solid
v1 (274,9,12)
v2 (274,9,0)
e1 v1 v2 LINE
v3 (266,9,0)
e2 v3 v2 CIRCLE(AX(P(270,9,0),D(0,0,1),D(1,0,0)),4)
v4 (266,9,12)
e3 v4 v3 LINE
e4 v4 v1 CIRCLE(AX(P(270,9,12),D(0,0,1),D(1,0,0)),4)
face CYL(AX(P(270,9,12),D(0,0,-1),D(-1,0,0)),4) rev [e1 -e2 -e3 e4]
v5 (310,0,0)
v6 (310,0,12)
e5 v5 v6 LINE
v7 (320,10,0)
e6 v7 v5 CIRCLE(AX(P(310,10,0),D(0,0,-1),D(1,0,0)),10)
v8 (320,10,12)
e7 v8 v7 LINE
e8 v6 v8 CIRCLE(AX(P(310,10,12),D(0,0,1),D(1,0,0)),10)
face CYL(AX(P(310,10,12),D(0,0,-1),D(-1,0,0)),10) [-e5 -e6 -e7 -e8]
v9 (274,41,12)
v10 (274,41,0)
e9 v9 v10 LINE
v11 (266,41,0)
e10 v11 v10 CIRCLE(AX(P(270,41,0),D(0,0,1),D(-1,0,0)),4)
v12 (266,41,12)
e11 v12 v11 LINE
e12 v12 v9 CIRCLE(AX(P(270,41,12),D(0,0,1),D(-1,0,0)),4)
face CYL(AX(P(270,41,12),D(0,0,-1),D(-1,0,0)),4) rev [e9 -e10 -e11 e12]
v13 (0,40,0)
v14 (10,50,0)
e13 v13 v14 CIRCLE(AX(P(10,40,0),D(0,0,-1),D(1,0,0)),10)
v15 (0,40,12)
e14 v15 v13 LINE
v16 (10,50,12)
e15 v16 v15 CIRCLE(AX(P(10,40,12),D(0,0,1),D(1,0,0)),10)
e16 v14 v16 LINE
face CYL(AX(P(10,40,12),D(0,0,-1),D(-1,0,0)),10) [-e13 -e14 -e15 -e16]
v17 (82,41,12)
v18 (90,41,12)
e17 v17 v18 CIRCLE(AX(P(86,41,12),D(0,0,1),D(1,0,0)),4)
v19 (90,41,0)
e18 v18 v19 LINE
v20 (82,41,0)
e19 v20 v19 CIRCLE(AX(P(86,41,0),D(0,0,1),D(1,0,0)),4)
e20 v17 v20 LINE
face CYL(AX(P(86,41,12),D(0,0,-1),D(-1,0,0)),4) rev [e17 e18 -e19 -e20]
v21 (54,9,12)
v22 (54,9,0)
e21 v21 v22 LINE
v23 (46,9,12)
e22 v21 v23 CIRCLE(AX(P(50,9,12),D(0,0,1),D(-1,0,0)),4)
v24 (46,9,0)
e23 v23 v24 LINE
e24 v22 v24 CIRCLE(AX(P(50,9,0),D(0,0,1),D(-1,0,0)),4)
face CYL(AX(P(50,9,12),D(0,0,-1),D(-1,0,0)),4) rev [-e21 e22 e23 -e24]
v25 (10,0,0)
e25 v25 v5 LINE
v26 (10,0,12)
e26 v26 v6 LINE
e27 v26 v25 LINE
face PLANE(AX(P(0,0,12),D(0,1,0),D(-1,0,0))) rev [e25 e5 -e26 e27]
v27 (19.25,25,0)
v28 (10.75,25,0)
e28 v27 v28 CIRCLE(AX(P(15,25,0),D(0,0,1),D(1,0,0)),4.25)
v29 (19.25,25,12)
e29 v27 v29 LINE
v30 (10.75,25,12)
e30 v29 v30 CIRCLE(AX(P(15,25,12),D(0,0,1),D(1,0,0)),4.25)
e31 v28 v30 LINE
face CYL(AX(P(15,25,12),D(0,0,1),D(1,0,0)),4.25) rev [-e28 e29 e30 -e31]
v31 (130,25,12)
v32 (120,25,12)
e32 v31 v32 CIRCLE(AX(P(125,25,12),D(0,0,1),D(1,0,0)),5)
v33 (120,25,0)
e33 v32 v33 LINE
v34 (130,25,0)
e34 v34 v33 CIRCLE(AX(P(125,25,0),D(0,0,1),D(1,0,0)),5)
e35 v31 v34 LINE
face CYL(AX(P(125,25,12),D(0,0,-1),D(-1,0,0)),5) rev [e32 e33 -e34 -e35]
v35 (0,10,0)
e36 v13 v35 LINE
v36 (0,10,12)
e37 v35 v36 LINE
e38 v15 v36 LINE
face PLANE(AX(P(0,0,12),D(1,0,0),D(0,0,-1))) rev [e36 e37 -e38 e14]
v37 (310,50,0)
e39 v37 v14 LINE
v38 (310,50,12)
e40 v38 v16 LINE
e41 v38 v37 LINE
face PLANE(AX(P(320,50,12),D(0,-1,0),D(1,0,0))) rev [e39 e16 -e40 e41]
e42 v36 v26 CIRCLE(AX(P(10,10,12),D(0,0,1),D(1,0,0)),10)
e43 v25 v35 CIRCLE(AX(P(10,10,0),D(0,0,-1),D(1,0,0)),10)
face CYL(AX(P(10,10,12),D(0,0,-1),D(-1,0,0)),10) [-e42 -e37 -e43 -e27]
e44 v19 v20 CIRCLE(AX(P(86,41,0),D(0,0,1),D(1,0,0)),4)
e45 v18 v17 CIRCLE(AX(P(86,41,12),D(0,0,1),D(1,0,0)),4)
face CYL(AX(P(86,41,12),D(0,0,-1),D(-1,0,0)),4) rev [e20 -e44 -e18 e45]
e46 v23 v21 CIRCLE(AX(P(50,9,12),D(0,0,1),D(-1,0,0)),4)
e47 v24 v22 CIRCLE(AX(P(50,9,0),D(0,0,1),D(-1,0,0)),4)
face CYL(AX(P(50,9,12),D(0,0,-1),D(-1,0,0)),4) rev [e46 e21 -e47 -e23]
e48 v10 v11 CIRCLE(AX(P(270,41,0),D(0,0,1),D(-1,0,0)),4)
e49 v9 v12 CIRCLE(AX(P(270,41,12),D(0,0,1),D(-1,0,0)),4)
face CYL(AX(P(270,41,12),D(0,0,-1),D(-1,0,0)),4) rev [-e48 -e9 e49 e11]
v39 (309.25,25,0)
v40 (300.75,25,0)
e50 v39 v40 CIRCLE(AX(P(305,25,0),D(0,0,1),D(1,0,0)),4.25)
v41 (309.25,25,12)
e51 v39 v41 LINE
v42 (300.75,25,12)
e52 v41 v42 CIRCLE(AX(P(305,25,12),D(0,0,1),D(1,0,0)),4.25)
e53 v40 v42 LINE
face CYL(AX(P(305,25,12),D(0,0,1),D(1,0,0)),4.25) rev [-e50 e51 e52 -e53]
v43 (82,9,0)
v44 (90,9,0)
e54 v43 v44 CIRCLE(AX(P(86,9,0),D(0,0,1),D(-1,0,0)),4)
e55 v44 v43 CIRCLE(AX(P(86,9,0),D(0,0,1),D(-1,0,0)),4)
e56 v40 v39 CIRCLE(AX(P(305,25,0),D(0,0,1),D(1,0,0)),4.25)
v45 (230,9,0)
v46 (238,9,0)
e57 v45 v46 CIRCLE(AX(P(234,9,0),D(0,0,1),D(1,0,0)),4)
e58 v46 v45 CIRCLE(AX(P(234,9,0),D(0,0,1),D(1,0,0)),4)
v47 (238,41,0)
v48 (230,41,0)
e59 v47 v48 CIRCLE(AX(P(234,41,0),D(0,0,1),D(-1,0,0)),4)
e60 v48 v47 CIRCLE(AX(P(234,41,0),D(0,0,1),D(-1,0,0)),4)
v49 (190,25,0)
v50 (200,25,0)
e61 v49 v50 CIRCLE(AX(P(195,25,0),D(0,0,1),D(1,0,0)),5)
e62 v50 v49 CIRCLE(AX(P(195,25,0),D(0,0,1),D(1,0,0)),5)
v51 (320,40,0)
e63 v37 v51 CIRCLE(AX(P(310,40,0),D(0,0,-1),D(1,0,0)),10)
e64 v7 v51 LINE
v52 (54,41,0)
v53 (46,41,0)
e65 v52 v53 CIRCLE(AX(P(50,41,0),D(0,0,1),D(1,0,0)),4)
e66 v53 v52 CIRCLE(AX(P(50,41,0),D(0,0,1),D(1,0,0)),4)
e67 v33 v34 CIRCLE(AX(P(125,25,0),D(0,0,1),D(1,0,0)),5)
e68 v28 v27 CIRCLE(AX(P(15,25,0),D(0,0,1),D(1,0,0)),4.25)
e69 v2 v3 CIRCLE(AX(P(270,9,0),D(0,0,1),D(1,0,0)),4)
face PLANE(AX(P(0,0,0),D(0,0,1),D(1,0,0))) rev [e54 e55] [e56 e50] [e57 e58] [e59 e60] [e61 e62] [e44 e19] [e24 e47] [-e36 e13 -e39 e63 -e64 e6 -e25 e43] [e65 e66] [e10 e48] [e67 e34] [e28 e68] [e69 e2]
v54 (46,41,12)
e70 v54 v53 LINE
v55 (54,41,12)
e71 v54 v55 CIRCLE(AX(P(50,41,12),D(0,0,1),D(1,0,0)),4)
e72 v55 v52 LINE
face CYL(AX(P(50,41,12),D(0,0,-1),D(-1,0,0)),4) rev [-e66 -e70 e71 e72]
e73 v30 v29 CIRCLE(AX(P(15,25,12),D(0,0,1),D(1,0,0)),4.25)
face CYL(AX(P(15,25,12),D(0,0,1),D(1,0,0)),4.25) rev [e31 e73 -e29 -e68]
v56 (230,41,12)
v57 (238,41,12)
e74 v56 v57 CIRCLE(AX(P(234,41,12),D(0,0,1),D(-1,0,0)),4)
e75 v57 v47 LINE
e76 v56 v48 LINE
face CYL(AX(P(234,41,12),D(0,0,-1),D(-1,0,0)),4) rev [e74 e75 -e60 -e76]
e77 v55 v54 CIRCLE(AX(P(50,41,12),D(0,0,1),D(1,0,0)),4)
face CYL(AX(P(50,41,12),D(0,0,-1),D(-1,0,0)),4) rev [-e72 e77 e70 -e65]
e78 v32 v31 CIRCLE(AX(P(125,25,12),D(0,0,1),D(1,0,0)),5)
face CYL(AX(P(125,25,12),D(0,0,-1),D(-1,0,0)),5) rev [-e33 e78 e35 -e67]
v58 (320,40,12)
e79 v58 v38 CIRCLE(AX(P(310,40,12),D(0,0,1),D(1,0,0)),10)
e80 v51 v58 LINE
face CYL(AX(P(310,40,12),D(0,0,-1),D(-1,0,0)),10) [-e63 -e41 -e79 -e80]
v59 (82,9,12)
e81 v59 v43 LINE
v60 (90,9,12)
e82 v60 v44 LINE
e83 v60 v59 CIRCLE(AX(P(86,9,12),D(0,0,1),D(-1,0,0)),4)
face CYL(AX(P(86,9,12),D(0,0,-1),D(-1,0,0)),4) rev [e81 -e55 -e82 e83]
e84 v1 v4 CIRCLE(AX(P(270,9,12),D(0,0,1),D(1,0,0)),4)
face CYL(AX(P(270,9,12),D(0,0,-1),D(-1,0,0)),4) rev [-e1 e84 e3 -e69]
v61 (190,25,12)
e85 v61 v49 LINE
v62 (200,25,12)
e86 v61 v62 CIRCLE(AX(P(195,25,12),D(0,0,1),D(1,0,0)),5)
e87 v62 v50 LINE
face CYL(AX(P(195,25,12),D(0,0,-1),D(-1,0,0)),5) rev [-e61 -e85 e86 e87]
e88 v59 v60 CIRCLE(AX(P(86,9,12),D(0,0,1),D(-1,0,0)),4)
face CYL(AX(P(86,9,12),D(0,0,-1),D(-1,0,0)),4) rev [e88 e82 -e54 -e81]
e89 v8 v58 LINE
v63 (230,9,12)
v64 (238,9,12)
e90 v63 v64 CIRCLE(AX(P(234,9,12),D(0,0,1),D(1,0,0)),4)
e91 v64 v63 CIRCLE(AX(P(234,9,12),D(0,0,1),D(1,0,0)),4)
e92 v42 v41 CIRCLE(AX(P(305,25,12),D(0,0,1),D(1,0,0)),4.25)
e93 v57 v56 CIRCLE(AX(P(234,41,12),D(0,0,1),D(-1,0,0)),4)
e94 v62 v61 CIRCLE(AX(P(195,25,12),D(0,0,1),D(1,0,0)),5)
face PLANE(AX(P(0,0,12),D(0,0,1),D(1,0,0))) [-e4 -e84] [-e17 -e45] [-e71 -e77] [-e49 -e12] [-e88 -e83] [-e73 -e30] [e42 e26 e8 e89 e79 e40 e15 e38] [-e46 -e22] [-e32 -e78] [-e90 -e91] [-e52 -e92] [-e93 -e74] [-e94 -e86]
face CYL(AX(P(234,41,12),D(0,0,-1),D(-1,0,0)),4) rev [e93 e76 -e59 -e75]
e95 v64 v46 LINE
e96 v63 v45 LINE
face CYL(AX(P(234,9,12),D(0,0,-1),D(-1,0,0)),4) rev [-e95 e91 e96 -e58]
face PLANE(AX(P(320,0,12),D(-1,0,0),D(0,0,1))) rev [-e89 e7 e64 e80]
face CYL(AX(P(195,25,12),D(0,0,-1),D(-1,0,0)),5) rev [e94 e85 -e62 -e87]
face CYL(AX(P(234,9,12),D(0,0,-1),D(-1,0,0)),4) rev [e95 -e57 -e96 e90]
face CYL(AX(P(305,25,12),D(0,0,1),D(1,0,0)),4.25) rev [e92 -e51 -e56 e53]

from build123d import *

# Parameters (mm, degrees)
SKETCH1_W              = 320
SKETCH1_H              = 50
SKETCH1_R              = 4
SKETCH1_R_2            = 5
BOSS_EXTRUDE1_DEPTH    = 12
M10_TAPPED_HOLE1_D     = 8.5
M10_TAPPED_HOLE1_DEPTH = 24.5
M10_TAPPED_HOLE1_TIP   = 2.553657631
FILLET1_R              = 10


with BuildPart() as part:
    # Sketch1 → Boss-Extrude1 (new body)
    with BuildSketch(Plane.XY):
        with Locations((160, 25)):
            Rectangle(SKETCH1_W, SKETCH1_H)
        with Locations((50, 41)):
            Circle(SKETCH1_R, mode=Mode.SUBTRACT)
        with Locations((86, 41)):
            Circle(SKETCH1_R, mode=Mode.SUBTRACT)
        with Locations(Location((86, 9, 0), (0, 0, 180))):
            Circle(SKETCH1_R, mode=Mode.SUBTRACT)
        with Locations(Location((50, 9, 0), (0, 0, 180))):
            Circle(SKETCH1_R, mode=Mode.SUBTRACT)
        with Locations((270, 9)):
            Circle(SKETCH1_R, mode=Mode.SUBTRACT)
        with Locations((234, 9)):
            Circle(SKETCH1_R, mode=Mode.SUBTRACT)
        with Locations(Location((234, 41, 0), (0, 0, 180))):
            Circle(SKETCH1_R, mode=Mode.SUBTRACT)
        with Locations(Location((270, 41, 0), (0, 0, 180))):
            Circle(SKETCH1_R, mode=Mode.SUBTRACT)
        with Locations((125, 25)):
            Circle(SKETCH1_R_2, mode=Mode.SUBTRACT)
        with Locations((195, 25)):
            Circle(SKETCH1_R_2, mode=Mode.SUBTRACT)
    extrude(amount=BOSS_EXTRUDE1_DEPTH)

    # M10 Tapped Hole1
    with Locations(Plane.XY.offset(12)):
        with Locations((15, 25), (305, 25)):
            Hole(M10_TAPPED_HOLE1_D / 2, depth=M10_TAPPED_HOLE1_DEPTH)
            with Locations((0, 0, -(M10_TAPPED_HOLE1_DEPTH + M10_TAPPED_HOLE1_TIP / 2))):  # 118° drill point
                Cone(0, M10_TAPPED_HOLE1_D / 2, M10_TAPPED_HOLE1_TIP, mode=Mode.SUBTRACT)

    # Fillet1
    fillet1_edges = [part.edges().sort_by_distance(p)[0] for p in [
        (320, 0, 6),
        (0, 0, 6),
        (0, 50, 6),
        (320, 50, 6),
    ]]
    fillet(fillet1_edges, radius=FILLET1_R)


solid = part.part
